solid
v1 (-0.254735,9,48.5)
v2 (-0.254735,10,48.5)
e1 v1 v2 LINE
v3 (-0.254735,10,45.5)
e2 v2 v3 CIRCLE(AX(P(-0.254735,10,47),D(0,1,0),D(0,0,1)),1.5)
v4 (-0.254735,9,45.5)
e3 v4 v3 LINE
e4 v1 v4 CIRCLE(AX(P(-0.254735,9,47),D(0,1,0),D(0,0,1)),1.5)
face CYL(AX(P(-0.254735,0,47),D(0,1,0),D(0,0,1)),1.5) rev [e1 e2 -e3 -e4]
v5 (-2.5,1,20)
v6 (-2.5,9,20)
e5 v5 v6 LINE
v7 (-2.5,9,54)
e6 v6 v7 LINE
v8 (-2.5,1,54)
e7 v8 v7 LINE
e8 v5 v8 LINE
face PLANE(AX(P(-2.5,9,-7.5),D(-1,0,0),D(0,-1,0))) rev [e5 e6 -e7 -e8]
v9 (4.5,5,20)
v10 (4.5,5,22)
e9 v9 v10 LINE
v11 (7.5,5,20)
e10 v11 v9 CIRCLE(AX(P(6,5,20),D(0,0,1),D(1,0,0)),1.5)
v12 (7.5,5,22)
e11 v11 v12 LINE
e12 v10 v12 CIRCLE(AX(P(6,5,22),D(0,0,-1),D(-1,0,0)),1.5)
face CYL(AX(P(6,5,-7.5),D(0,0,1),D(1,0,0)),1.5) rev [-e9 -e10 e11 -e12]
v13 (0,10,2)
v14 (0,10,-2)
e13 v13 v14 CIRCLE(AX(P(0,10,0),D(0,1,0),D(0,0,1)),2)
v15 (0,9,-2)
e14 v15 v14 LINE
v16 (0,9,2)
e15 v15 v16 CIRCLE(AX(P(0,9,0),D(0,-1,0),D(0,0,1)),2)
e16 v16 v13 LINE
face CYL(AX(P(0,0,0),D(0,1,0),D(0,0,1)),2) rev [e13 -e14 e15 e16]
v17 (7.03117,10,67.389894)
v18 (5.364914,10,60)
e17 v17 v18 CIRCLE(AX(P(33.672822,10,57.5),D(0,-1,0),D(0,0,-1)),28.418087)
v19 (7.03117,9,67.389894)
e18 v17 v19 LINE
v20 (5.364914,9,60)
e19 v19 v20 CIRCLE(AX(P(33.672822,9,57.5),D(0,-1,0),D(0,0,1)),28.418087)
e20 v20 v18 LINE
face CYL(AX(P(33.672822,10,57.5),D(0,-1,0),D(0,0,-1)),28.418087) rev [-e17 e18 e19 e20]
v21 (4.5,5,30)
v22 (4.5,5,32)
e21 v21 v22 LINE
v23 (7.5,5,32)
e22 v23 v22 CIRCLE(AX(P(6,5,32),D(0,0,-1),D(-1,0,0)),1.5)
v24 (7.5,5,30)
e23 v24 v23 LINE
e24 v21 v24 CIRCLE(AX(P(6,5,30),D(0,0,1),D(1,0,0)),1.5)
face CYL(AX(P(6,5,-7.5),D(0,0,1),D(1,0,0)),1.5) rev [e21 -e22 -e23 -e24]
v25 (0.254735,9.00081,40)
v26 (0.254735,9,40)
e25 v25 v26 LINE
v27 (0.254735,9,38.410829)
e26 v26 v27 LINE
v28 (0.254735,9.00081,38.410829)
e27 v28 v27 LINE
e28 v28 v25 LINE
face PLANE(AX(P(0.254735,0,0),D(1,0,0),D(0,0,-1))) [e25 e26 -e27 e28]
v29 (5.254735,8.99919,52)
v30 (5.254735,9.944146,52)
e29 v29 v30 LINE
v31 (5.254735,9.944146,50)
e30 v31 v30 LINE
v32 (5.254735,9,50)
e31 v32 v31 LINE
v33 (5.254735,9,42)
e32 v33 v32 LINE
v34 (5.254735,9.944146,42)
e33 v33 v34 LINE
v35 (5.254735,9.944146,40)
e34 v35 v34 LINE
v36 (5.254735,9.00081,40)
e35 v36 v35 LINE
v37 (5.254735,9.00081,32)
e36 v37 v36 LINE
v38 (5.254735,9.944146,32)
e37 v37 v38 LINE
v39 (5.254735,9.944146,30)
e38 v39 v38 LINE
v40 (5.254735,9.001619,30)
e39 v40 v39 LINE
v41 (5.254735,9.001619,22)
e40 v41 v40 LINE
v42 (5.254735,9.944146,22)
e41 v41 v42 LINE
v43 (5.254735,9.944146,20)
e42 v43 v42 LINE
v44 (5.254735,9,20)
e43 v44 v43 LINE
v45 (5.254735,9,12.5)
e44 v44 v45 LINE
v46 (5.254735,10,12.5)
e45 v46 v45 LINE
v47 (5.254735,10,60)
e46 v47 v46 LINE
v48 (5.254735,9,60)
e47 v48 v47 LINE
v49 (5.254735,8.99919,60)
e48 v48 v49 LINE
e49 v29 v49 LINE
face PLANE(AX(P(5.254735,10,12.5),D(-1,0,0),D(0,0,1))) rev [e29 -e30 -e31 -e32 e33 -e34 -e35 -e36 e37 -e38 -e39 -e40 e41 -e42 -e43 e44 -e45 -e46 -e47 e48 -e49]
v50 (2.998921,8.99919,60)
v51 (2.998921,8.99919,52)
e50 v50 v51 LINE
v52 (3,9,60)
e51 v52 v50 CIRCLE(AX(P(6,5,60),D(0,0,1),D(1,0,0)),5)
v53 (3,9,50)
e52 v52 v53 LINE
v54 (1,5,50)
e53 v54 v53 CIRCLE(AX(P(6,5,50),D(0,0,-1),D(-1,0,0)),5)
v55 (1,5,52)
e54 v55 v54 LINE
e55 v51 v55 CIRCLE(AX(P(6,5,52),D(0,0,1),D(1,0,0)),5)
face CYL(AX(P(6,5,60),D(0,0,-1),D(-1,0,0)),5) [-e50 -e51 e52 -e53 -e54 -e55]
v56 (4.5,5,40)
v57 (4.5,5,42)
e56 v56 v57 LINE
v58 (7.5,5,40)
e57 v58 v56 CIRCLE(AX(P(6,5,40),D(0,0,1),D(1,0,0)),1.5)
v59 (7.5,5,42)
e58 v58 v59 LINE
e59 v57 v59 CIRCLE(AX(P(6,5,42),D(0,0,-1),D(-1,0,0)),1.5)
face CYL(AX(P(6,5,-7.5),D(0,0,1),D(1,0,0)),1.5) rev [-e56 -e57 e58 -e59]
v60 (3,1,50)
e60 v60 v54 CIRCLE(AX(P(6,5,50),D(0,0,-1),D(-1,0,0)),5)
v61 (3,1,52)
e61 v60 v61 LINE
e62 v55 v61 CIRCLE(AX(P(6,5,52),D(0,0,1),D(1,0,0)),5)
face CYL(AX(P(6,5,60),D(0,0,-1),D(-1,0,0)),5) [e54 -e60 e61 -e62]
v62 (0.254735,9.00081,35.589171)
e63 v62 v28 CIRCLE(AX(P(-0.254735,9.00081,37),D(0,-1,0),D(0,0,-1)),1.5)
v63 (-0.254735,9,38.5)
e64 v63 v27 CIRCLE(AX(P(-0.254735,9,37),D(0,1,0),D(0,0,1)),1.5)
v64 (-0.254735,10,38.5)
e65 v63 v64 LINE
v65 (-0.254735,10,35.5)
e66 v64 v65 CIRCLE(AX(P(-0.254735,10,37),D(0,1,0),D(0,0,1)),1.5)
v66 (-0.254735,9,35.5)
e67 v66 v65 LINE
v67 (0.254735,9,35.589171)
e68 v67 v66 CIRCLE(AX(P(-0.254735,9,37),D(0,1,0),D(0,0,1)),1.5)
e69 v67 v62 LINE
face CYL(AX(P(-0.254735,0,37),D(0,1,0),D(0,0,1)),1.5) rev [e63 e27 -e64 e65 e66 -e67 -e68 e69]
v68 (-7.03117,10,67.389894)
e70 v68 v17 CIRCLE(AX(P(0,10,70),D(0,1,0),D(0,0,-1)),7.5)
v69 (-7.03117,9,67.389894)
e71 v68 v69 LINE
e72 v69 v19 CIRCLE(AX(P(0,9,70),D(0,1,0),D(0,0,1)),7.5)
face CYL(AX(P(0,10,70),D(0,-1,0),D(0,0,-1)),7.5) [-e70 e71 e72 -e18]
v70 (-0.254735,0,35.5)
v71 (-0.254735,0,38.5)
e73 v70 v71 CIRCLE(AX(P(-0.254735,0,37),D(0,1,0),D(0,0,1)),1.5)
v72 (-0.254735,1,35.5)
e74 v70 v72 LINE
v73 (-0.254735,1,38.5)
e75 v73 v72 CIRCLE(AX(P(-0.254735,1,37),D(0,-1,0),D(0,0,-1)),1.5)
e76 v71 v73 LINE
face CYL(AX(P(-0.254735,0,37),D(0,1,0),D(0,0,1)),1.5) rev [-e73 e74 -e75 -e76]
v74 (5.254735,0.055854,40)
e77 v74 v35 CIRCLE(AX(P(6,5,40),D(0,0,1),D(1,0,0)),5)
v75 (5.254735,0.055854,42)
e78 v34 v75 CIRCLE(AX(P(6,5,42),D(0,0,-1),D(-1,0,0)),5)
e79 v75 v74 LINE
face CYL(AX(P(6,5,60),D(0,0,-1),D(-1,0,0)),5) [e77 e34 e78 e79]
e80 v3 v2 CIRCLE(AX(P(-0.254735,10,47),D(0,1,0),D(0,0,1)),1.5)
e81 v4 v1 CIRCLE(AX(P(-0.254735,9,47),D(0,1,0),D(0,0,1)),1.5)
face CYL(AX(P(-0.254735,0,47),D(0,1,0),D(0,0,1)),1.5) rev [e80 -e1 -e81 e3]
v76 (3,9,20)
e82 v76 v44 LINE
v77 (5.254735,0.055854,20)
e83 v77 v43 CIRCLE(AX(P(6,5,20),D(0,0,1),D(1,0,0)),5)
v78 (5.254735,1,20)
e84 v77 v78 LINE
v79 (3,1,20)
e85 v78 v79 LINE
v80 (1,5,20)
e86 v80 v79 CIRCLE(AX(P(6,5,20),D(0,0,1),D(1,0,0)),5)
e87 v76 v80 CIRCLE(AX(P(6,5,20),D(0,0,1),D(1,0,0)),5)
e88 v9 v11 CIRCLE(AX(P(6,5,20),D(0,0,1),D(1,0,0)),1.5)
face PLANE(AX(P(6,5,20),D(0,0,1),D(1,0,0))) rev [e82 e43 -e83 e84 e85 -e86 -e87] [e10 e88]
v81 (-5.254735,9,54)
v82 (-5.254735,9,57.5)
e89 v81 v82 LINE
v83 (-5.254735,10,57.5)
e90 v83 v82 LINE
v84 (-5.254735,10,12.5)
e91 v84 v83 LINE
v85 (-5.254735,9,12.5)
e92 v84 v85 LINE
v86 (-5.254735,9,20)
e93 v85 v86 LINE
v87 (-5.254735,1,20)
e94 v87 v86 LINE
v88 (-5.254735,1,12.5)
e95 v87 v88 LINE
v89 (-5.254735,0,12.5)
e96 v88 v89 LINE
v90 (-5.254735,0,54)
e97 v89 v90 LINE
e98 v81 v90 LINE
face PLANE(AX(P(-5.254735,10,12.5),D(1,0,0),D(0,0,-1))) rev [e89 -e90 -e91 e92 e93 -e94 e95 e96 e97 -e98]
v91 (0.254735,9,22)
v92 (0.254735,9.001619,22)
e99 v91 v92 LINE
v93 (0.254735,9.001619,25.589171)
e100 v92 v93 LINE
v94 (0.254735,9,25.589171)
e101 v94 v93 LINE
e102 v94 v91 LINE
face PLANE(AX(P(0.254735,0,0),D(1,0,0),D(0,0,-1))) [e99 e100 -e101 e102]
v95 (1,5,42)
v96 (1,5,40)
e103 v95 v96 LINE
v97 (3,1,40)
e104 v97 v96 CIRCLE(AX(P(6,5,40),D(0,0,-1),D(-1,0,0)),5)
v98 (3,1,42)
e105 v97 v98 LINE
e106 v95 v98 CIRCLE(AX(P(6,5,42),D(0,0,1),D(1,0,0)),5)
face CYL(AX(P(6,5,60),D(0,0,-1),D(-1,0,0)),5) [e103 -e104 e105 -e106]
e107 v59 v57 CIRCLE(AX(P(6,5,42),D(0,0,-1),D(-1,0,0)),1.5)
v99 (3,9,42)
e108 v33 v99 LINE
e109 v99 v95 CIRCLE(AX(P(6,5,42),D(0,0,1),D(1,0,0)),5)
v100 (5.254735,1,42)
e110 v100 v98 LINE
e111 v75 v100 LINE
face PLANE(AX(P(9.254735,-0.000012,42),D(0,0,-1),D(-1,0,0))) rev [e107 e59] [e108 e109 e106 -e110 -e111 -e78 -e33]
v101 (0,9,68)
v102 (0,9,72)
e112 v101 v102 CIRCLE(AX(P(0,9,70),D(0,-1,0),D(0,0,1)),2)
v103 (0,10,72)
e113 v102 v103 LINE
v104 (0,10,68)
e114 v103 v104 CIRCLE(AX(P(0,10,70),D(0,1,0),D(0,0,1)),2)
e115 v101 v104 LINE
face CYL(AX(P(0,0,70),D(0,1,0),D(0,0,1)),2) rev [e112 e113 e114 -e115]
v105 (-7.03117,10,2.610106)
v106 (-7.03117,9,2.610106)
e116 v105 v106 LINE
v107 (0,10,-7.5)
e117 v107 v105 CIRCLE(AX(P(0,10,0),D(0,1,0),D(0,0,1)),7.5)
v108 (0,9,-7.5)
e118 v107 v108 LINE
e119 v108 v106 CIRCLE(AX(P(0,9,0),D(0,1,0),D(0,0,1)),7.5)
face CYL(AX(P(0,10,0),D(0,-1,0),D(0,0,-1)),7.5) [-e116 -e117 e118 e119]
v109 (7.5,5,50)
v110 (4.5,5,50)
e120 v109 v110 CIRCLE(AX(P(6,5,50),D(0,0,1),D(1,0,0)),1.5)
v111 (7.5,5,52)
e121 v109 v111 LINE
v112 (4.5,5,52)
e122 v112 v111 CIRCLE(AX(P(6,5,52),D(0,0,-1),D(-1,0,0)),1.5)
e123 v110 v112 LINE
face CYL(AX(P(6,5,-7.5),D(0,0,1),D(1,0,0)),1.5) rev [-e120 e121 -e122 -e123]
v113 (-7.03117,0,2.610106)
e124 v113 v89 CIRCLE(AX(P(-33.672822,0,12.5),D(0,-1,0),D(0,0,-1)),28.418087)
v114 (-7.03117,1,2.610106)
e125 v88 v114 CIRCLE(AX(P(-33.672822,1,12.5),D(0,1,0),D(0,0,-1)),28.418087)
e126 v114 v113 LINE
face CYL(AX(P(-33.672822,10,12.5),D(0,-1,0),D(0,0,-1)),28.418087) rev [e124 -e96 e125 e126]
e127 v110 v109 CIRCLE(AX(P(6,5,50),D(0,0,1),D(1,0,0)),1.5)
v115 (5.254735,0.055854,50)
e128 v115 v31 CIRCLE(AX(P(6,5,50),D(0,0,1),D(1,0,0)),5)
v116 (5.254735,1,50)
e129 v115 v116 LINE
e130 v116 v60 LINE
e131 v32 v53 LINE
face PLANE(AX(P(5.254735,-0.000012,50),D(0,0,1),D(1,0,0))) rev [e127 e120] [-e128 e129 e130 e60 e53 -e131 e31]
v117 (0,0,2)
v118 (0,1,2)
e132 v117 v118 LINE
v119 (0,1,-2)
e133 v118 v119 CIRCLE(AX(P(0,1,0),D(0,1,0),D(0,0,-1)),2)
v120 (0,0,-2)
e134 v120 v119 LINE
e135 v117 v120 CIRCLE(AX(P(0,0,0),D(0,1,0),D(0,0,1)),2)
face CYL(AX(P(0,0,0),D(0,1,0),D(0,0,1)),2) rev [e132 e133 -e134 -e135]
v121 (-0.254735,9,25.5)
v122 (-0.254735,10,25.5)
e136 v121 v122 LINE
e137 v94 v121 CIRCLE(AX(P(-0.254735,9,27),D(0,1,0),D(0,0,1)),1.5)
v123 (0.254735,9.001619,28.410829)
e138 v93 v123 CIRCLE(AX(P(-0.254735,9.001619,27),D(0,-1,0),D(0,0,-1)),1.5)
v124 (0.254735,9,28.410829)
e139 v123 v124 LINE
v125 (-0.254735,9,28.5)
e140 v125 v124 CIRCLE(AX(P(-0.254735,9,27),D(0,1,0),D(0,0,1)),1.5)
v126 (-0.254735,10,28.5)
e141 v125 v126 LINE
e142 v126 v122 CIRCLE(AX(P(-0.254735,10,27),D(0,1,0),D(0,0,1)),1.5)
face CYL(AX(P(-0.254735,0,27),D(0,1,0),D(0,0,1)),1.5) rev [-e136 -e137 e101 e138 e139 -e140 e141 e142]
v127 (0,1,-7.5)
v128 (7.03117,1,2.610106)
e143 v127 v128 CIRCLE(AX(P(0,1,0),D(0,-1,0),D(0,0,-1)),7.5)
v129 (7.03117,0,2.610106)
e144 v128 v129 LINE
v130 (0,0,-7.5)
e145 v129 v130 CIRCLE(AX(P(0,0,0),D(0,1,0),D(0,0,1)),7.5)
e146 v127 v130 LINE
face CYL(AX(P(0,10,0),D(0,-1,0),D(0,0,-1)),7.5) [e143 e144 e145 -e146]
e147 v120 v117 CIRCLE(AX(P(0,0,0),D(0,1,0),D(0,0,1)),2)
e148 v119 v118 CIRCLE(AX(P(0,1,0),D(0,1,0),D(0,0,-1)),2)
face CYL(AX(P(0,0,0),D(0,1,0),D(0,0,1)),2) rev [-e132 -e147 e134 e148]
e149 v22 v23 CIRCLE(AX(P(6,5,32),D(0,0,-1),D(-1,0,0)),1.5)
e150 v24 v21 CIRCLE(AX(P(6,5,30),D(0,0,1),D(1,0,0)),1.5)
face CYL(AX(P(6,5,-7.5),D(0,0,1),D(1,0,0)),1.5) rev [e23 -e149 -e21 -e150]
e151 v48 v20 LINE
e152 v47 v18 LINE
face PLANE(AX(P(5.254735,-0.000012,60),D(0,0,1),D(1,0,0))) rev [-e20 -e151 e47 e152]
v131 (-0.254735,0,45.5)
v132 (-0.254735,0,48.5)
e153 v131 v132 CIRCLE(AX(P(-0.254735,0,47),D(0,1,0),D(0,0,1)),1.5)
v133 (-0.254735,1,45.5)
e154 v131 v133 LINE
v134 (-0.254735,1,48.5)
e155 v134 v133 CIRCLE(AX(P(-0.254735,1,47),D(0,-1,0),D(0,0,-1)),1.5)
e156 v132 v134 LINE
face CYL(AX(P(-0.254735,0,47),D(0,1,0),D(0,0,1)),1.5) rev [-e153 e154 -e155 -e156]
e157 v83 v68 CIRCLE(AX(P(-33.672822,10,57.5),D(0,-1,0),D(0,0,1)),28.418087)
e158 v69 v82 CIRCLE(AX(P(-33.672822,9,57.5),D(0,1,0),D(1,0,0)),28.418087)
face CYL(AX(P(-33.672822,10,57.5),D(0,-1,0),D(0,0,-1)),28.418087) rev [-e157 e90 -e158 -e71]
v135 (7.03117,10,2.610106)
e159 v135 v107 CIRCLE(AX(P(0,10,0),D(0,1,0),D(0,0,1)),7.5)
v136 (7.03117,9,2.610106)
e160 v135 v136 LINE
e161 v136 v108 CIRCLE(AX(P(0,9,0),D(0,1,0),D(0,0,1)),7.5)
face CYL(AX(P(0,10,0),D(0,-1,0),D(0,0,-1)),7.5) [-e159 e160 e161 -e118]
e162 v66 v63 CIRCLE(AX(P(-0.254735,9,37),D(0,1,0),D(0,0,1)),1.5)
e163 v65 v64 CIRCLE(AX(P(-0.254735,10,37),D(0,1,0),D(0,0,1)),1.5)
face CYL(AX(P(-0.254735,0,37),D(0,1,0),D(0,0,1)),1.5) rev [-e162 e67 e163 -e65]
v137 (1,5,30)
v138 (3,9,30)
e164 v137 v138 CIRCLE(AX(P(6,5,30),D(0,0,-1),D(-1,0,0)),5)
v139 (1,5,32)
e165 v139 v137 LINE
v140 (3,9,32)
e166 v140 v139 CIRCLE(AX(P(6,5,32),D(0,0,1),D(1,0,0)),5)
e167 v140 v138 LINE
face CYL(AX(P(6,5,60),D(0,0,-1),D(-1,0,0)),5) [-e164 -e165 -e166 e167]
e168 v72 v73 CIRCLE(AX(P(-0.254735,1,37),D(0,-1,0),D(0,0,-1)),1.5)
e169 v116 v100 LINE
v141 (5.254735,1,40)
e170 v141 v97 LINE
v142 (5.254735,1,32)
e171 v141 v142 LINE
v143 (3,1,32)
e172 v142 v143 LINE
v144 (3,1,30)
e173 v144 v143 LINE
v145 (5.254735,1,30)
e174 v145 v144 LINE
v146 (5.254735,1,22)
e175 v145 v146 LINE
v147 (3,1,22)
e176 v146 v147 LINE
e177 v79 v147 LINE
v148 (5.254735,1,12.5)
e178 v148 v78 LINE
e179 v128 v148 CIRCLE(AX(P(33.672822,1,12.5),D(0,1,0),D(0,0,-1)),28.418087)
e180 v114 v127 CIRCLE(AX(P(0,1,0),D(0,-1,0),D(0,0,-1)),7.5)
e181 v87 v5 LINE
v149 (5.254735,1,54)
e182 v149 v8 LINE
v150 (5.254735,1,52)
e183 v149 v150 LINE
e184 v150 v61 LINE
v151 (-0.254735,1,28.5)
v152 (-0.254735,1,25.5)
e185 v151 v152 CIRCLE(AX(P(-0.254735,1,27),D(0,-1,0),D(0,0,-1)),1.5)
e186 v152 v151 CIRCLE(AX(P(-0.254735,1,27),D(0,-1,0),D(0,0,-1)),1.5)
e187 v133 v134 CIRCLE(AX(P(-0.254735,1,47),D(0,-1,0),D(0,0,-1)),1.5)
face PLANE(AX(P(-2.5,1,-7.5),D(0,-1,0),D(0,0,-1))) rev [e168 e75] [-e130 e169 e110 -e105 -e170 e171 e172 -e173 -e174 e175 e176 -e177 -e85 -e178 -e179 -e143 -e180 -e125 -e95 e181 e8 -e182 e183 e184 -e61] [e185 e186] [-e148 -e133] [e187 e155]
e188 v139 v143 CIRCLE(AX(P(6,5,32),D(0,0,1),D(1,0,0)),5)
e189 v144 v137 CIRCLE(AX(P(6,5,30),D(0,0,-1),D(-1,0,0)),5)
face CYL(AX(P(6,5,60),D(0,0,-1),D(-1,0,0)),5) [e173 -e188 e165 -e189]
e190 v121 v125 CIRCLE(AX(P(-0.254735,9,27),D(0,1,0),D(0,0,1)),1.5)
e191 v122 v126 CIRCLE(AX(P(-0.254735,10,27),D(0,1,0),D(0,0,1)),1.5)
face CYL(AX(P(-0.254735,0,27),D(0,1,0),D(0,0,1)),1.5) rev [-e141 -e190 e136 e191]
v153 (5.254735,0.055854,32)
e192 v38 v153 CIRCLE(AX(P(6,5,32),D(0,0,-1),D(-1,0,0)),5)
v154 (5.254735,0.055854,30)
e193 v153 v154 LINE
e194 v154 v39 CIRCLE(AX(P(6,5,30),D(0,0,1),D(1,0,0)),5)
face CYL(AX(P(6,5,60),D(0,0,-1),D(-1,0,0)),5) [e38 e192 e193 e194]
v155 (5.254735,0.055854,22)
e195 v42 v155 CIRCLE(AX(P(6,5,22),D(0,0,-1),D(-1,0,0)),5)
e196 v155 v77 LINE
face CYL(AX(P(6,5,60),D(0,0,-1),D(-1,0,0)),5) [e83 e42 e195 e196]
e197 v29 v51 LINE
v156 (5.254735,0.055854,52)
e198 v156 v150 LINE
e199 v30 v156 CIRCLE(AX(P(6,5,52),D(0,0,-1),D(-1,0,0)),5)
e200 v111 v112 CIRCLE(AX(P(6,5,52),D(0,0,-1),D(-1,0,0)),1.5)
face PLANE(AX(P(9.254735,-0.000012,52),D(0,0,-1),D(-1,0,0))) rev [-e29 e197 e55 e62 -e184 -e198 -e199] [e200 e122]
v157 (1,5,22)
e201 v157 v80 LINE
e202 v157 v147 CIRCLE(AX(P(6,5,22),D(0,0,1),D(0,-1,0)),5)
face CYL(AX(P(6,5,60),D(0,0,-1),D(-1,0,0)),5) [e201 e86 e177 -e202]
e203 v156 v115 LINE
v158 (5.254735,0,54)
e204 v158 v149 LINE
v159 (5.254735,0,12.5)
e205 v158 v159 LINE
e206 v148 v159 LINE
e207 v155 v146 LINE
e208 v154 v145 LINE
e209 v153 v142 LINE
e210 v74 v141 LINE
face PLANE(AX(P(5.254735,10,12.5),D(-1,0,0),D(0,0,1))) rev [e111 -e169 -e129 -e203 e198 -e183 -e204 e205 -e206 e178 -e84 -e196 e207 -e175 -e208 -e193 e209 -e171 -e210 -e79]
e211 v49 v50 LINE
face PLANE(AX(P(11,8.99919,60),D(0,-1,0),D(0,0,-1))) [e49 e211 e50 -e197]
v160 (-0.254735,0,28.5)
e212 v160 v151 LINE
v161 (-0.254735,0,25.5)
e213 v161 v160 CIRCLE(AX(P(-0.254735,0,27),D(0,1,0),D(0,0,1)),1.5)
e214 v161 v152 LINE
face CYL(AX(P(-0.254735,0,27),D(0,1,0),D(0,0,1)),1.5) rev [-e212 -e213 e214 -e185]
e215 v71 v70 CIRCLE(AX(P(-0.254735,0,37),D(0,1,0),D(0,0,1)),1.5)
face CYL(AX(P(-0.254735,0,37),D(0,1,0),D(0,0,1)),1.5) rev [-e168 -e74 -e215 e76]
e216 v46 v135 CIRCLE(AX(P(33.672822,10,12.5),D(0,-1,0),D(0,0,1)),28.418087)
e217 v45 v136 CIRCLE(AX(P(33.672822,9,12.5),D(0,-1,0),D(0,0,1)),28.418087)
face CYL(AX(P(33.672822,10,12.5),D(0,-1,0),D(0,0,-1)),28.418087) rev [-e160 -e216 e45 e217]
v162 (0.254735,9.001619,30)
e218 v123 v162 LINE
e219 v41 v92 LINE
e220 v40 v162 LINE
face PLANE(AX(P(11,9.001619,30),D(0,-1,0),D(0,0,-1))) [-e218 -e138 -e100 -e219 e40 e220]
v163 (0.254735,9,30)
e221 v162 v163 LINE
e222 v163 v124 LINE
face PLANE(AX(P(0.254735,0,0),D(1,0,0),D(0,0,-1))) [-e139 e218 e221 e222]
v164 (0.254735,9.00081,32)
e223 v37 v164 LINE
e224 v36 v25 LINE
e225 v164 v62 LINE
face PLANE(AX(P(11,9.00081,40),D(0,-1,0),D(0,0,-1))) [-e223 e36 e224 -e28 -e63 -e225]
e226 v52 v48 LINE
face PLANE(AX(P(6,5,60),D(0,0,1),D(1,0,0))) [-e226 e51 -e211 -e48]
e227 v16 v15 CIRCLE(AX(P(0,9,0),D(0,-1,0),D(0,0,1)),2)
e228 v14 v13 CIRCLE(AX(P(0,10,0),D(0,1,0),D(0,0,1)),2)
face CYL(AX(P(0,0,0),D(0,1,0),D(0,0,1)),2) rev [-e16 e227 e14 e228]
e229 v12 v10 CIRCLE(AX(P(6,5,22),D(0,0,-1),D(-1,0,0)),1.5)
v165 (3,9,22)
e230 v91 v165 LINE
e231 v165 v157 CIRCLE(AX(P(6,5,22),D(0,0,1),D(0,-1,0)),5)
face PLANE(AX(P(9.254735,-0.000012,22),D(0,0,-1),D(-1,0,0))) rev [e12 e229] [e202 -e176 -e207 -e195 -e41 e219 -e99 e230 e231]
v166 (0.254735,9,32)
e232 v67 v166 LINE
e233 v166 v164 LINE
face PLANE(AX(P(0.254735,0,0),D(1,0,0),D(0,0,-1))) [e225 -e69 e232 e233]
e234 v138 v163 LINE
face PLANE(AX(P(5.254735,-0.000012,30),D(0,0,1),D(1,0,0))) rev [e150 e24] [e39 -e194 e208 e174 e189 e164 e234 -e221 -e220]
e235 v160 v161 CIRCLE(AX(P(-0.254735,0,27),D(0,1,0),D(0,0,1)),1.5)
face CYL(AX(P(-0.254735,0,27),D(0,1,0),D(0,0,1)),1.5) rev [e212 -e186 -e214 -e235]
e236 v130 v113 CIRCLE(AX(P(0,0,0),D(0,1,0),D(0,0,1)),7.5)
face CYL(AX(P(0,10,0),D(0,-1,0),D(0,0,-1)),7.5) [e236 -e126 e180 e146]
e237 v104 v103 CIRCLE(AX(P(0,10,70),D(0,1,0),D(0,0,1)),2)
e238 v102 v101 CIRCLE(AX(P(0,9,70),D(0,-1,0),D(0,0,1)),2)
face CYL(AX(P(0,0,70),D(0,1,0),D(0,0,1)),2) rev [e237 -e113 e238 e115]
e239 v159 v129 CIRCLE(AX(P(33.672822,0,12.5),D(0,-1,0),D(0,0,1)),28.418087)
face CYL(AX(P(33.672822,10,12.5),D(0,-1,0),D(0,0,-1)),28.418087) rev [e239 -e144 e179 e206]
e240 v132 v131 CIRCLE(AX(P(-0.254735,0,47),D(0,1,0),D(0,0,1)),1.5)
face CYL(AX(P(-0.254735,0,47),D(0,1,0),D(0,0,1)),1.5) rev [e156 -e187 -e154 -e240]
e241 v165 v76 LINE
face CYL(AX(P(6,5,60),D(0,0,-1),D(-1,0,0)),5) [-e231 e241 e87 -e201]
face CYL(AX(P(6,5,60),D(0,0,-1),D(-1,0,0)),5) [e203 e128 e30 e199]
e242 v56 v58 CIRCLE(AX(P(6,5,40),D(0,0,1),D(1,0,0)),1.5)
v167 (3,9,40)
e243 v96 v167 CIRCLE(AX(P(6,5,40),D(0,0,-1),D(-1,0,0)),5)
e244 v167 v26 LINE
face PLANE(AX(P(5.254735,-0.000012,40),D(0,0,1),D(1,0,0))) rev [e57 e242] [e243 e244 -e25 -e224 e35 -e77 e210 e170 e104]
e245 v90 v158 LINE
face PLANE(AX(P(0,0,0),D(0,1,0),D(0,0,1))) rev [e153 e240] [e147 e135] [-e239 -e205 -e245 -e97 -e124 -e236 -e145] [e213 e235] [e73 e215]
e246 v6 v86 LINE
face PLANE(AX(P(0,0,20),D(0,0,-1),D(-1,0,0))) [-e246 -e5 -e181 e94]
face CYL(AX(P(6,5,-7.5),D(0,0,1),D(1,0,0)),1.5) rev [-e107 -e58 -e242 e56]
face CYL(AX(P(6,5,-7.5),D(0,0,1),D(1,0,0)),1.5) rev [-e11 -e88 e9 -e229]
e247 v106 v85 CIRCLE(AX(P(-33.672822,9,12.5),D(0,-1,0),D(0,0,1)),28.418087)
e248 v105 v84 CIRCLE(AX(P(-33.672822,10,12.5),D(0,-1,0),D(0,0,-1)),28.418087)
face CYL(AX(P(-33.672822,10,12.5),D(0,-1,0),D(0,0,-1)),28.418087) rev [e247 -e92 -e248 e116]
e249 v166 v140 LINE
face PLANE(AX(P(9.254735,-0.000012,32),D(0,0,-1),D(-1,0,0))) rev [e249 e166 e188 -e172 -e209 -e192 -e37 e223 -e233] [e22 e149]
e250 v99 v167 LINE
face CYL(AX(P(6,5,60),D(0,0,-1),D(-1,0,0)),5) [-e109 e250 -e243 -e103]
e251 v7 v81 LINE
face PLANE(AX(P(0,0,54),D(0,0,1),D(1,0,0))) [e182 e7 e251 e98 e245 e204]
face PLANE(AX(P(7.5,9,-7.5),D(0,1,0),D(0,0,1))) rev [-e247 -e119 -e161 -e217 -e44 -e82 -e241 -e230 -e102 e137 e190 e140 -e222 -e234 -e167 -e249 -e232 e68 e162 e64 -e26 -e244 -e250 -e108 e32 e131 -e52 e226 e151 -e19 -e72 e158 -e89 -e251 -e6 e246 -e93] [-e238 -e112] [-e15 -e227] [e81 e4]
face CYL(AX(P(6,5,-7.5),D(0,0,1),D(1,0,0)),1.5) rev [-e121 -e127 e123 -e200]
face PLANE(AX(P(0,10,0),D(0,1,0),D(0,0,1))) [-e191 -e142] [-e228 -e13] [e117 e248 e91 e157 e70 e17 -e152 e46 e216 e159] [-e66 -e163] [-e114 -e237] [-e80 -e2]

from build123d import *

# Parameters (mm, degrees)
BOSS_EXTRUDE1_DEPTH     = 10
CUT_EXTRUDE1_DEPTH      = 79.501592341
CUT_EXTRUDE1_DEPTH_BACK = 79.501592341
SKETCH2_R               = 2
CUT_EXTRUDE4_DEPTH      = 79.501592341
CUT_EXTRUDE4_DEPTH_BACK = 79.501592341
SKETCH5_W               = 10
SKETCH5_H               = 8
SKETCH3_R               = 5
BOSS_EXTRUDE2_DEPTH     = 40
CUT_EXTRUDE3_DEPTH      = 79.912926724
CUT_EXTRUDE3_DEPTH_BACK = 79.912926724
SKETCH4_W               = 4
SKETCH4_H               = 8
CUT_EXTRUDE5_DEPTH      = 80.176595509
CUT_EXTRUDE5_DEPTH_BACK = 5
SKETCH6_W               = 8
SKETCH6_H               = 7.999190419
SKETCH6_H_2             = 8
SKETCH6_H_3             = 8.000809581
SKETCH6_H_4             = 8.001619162
SKETCH7_W               = 5
SKETCH7_H               = 8
CUT_EXTRUDE6_DEPTH      = 60.390655831
CUT_EXTRUDE8_DEPTH      = 79.912926698
CUT_EXTRUDE8_DEPTH_BACK = 79.912926698
SKETCH9_R               = 1.5
CUT_EXTRUDE9_DEPTH      = 62.329030646
CUT_EXTRUDE9_DEPTH_BACK = 62.329030646
SKETCH10_R              = 1.5
SKETCH11_W              = 18
SKETCH11_H              = 9
CUT_EXTRUDE10_DEPTH     = 70.117653317
CUT_EXTRUDE11_DEPTH     = 6


with BuildPart() as part:
    # Sketch1 → Boss-Extrude1 (new body)
    with BuildSketch(Plane(origin=(0, 0, 0), x_dir=(1, 0, 0), z_dir=(0, 1, 0))):
        with BuildLine():
            Line((-5.254735448, -12.5), (-5.254735448, -57.5))
            ThreePointArc((-5.254735448, -57.5), (-5.702369539, -62.524085228), (-7.031169787, -67.389894366))
            ThreePointArc((-7.031169787, -67.389894366), (-7.381862008, -68.674061352), (-7.5, -70))
            ThreePointArc((-7.5, -70), (0, -77.5), (7.5, -70))
            ThreePointArc((7.5, -70), (7.381862008, -68.674061352), (7.031169787, -67.389894366))
            ThreePointArc((7.031169787, -67.389894366), (5.702369539, -62.524085228), (5.254735448, -57.5))
            Line((5.254735448, -57.5), (5.254735448, -12.5))
            ThreePointArc((5.254735448, -12.5), (5.702369539, -7.475914772), (7.031169787, -2.610105634))
            ThreePointArc((7.031169787, -2.610105634), (7.381862008, -1.325938648), (7.5, 0))
            ThreePointArc((7.5, 0), (0, 7.5), (-7.5, 0))
            ThreePointArc((-7.5, 0), (-7.381862008, -1.325938648), (-7.031169787, -2.610105634))
            ThreePointArc((-7.031169787, -2.610105634), (-5.702369539, -7.475914772), (-5.254735448, -12.5))
        make_face()
    extrude(amount=BOSS_EXTRUDE1_DEPTH)

    # Sketch2 → Cut-Extrude1 (cut, two sides: drawn at the far end of the back side and taken through both)
    with BuildSketch(Plane(origin=(0, 10, 0), x_dir=(1, 0, 0), z_dir=(0, 1, 0)).offset(-CUT_EXTRUDE1_DEPTH_BACK)):
        with Locations(Location((0, 0, 0), (0, 0, 270))):
            Circle(SKETCH2_R)
        with Locations(Location((0, -70, 0), (0, 0, 270))):
            Circle(SKETCH2_R)
    extrude(amount=CUT_EXTRUDE1_DEPTH + CUT_EXTRUDE1_DEPTH_BACK, mode=Mode.SUBTRACT)

    # Sketch5 → Cut-Extrude4 (cut, two sides: drawn at the far end of the back side and taken through both)
    with BuildSketch(Plane.XY.offset(-CUT_EXTRUDE4_DEPTH_BACK)):
        with Locations((2.5, 5)):
            Rectangle(SKETCH5_W, SKETCH5_H)
    extrude(amount=CUT_EXTRUDE4_DEPTH + CUT_EXTRUDE4_DEPTH_BACK, mode=Mode.SUBTRACT)

    # Sketch3 → Boss-Extrude2 (add)
    with BuildSketch(Plane.XY.offset(20)):
        with Locations((6, 5)):
            Circle(SKETCH3_R)
    extrude(amount=BOSS_EXTRUDE2_DEPTH)

    # Sketch4 → Cut-Extrude3 (cut, two sides: drawn at the far end of the back side and taken through both)
    with BuildSketch(Plane(origin=(0, 0, 0), x_dir=(1, 0, 0), z_dir=(0, 1, 0)).offset(-CUT_EXTRUDE3_DEPTH_BACK)):
        with Locations((7.254735448, -26)):
            Rectangle(SKETCH4_W, SKETCH4_H)
        with Locations((7.254735448, -36)):
            Rectangle(SKETCH4_W, SKETCH4_H)
        with Locations((7.254735448, -46)):
            Rectangle(SKETCH4_W, SKETCH4_H)
        with Locations((7.254735448, -56)):
            Rectangle(SKETCH4_W, SKETCH4_H)
    extrude(amount=CUT_EXTRUDE3_DEPTH + CUT_EXTRUDE3_DEPTH_BACK, mode=Mode.SUBTRACT)

    # Sketch6 → Cut-Extrude5 (cut, two sides: drawn at the far end of the back side and taken through both)
    with BuildSketch(Plane(origin=(5.254735448, 0, 0), x_dir=(0, 0, -1), z_dir=(1, 0, 0)).offset(-CUT_EXTRUDE5_DEPTH_BACK)):
        with Locations((-56, 4.99959521)):
            Rectangle(SKETCH6_W, SKETCH6_H)
        with Locations((-46, 5)):
            Rectangle(SKETCH6_W, SKETCH6_H_2)
        with Locations((-36, 5.000404791)):
            Rectangle(SKETCH6_W, SKETCH6_H_3)
        with Locations((-26, 5.000809581)):
            Rectangle(SKETCH6_W, SKETCH6_H_4)
    extrude(amount=CUT_EXTRUDE5_DEPTH + CUT_EXTRUDE5_DEPTH_BACK, mode=Mode.SUBTRACT)

    # Sketch7 → Cut-Extrude6 (cut, through all)
    with BuildSketch(Plane.XY.offset(20)):
        with Locations((-5, 5)):
            Rectangle(SKETCH7_W, SKETCH7_H)
    extrude(amount=-CUT_EXTRUDE6_DEPTH, mode=Mode.SUBTRACT)

    # Sketch9 → Cut-Extrude8 (cut, two sides: drawn at the far end of the back side and taken through both)
    with BuildSketch(Plane(origin=(0, 10, 0), x_dir=(1, 0, 0), z_dir=(0, 1, 0)).offset(-CUT_EXTRUDE8_DEPTH_BACK)):
        with Locations(Location((-0.254735448, -27, 0), (0, 0, 270))):
            Circle(SKETCH9_R)
        with Locations(Location((-0.254735448, -37, 0), (0, 0, 270))):
            Circle(SKETCH9_R)
        with Locations(Location((-0.254735448, -47, 0), (0, 0, 270))):
            Circle(SKETCH9_R)
    extrude(amount=CUT_EXTRUDE8_DEPTH + CUT_EXTRUDE8_DEPTH_BACK, mode=Mode.SUBTRACT)

    # Sketch10 → Cut-Extrude9 (cut, two sides: drawn at the far end of the back side and taken through both)
    with BuildSketch(Plane.XY.offset(52).offset(-CUT_EXTRUDE9_DEPTH_BACK)):
        with Locations((6, 5)):
            Circle(SKETCH10_R)
    extrude(amount=CUT_EXTRUDE9_DEPTH + CUT_EXTRUDE9_DEPTH_BACK, mode=Mode.SUBTRACT)

    # Sketch11 → Cut-Extrude10 (cut, through all)
    with BuildSketch(Plane.XY.offset(60)):
        with Locations((-0.335498684, 4.5)):
            Rectangle(SKETCH11_W, SKETCH11_H)
    extrude(amount=CUT_EXTRUDE10_DEPTH, mode=Mode.SUBTRACT)

    # Sketch12 → Cut-Extrude11 (cut)
    with BuildSketch(Plane.XY.offset(60)):
        Polygon((5.254735448, 0), (5.254735448, 1), (-2.5, 1), (-2.5, 9), (-5.364914213, 9), (-5.364914213, 0), align=None)
    extrude(amount=-CUT_EXTRUDE11_DEPTH, mode=Mode.SUBTRACT)


solid = part.part
